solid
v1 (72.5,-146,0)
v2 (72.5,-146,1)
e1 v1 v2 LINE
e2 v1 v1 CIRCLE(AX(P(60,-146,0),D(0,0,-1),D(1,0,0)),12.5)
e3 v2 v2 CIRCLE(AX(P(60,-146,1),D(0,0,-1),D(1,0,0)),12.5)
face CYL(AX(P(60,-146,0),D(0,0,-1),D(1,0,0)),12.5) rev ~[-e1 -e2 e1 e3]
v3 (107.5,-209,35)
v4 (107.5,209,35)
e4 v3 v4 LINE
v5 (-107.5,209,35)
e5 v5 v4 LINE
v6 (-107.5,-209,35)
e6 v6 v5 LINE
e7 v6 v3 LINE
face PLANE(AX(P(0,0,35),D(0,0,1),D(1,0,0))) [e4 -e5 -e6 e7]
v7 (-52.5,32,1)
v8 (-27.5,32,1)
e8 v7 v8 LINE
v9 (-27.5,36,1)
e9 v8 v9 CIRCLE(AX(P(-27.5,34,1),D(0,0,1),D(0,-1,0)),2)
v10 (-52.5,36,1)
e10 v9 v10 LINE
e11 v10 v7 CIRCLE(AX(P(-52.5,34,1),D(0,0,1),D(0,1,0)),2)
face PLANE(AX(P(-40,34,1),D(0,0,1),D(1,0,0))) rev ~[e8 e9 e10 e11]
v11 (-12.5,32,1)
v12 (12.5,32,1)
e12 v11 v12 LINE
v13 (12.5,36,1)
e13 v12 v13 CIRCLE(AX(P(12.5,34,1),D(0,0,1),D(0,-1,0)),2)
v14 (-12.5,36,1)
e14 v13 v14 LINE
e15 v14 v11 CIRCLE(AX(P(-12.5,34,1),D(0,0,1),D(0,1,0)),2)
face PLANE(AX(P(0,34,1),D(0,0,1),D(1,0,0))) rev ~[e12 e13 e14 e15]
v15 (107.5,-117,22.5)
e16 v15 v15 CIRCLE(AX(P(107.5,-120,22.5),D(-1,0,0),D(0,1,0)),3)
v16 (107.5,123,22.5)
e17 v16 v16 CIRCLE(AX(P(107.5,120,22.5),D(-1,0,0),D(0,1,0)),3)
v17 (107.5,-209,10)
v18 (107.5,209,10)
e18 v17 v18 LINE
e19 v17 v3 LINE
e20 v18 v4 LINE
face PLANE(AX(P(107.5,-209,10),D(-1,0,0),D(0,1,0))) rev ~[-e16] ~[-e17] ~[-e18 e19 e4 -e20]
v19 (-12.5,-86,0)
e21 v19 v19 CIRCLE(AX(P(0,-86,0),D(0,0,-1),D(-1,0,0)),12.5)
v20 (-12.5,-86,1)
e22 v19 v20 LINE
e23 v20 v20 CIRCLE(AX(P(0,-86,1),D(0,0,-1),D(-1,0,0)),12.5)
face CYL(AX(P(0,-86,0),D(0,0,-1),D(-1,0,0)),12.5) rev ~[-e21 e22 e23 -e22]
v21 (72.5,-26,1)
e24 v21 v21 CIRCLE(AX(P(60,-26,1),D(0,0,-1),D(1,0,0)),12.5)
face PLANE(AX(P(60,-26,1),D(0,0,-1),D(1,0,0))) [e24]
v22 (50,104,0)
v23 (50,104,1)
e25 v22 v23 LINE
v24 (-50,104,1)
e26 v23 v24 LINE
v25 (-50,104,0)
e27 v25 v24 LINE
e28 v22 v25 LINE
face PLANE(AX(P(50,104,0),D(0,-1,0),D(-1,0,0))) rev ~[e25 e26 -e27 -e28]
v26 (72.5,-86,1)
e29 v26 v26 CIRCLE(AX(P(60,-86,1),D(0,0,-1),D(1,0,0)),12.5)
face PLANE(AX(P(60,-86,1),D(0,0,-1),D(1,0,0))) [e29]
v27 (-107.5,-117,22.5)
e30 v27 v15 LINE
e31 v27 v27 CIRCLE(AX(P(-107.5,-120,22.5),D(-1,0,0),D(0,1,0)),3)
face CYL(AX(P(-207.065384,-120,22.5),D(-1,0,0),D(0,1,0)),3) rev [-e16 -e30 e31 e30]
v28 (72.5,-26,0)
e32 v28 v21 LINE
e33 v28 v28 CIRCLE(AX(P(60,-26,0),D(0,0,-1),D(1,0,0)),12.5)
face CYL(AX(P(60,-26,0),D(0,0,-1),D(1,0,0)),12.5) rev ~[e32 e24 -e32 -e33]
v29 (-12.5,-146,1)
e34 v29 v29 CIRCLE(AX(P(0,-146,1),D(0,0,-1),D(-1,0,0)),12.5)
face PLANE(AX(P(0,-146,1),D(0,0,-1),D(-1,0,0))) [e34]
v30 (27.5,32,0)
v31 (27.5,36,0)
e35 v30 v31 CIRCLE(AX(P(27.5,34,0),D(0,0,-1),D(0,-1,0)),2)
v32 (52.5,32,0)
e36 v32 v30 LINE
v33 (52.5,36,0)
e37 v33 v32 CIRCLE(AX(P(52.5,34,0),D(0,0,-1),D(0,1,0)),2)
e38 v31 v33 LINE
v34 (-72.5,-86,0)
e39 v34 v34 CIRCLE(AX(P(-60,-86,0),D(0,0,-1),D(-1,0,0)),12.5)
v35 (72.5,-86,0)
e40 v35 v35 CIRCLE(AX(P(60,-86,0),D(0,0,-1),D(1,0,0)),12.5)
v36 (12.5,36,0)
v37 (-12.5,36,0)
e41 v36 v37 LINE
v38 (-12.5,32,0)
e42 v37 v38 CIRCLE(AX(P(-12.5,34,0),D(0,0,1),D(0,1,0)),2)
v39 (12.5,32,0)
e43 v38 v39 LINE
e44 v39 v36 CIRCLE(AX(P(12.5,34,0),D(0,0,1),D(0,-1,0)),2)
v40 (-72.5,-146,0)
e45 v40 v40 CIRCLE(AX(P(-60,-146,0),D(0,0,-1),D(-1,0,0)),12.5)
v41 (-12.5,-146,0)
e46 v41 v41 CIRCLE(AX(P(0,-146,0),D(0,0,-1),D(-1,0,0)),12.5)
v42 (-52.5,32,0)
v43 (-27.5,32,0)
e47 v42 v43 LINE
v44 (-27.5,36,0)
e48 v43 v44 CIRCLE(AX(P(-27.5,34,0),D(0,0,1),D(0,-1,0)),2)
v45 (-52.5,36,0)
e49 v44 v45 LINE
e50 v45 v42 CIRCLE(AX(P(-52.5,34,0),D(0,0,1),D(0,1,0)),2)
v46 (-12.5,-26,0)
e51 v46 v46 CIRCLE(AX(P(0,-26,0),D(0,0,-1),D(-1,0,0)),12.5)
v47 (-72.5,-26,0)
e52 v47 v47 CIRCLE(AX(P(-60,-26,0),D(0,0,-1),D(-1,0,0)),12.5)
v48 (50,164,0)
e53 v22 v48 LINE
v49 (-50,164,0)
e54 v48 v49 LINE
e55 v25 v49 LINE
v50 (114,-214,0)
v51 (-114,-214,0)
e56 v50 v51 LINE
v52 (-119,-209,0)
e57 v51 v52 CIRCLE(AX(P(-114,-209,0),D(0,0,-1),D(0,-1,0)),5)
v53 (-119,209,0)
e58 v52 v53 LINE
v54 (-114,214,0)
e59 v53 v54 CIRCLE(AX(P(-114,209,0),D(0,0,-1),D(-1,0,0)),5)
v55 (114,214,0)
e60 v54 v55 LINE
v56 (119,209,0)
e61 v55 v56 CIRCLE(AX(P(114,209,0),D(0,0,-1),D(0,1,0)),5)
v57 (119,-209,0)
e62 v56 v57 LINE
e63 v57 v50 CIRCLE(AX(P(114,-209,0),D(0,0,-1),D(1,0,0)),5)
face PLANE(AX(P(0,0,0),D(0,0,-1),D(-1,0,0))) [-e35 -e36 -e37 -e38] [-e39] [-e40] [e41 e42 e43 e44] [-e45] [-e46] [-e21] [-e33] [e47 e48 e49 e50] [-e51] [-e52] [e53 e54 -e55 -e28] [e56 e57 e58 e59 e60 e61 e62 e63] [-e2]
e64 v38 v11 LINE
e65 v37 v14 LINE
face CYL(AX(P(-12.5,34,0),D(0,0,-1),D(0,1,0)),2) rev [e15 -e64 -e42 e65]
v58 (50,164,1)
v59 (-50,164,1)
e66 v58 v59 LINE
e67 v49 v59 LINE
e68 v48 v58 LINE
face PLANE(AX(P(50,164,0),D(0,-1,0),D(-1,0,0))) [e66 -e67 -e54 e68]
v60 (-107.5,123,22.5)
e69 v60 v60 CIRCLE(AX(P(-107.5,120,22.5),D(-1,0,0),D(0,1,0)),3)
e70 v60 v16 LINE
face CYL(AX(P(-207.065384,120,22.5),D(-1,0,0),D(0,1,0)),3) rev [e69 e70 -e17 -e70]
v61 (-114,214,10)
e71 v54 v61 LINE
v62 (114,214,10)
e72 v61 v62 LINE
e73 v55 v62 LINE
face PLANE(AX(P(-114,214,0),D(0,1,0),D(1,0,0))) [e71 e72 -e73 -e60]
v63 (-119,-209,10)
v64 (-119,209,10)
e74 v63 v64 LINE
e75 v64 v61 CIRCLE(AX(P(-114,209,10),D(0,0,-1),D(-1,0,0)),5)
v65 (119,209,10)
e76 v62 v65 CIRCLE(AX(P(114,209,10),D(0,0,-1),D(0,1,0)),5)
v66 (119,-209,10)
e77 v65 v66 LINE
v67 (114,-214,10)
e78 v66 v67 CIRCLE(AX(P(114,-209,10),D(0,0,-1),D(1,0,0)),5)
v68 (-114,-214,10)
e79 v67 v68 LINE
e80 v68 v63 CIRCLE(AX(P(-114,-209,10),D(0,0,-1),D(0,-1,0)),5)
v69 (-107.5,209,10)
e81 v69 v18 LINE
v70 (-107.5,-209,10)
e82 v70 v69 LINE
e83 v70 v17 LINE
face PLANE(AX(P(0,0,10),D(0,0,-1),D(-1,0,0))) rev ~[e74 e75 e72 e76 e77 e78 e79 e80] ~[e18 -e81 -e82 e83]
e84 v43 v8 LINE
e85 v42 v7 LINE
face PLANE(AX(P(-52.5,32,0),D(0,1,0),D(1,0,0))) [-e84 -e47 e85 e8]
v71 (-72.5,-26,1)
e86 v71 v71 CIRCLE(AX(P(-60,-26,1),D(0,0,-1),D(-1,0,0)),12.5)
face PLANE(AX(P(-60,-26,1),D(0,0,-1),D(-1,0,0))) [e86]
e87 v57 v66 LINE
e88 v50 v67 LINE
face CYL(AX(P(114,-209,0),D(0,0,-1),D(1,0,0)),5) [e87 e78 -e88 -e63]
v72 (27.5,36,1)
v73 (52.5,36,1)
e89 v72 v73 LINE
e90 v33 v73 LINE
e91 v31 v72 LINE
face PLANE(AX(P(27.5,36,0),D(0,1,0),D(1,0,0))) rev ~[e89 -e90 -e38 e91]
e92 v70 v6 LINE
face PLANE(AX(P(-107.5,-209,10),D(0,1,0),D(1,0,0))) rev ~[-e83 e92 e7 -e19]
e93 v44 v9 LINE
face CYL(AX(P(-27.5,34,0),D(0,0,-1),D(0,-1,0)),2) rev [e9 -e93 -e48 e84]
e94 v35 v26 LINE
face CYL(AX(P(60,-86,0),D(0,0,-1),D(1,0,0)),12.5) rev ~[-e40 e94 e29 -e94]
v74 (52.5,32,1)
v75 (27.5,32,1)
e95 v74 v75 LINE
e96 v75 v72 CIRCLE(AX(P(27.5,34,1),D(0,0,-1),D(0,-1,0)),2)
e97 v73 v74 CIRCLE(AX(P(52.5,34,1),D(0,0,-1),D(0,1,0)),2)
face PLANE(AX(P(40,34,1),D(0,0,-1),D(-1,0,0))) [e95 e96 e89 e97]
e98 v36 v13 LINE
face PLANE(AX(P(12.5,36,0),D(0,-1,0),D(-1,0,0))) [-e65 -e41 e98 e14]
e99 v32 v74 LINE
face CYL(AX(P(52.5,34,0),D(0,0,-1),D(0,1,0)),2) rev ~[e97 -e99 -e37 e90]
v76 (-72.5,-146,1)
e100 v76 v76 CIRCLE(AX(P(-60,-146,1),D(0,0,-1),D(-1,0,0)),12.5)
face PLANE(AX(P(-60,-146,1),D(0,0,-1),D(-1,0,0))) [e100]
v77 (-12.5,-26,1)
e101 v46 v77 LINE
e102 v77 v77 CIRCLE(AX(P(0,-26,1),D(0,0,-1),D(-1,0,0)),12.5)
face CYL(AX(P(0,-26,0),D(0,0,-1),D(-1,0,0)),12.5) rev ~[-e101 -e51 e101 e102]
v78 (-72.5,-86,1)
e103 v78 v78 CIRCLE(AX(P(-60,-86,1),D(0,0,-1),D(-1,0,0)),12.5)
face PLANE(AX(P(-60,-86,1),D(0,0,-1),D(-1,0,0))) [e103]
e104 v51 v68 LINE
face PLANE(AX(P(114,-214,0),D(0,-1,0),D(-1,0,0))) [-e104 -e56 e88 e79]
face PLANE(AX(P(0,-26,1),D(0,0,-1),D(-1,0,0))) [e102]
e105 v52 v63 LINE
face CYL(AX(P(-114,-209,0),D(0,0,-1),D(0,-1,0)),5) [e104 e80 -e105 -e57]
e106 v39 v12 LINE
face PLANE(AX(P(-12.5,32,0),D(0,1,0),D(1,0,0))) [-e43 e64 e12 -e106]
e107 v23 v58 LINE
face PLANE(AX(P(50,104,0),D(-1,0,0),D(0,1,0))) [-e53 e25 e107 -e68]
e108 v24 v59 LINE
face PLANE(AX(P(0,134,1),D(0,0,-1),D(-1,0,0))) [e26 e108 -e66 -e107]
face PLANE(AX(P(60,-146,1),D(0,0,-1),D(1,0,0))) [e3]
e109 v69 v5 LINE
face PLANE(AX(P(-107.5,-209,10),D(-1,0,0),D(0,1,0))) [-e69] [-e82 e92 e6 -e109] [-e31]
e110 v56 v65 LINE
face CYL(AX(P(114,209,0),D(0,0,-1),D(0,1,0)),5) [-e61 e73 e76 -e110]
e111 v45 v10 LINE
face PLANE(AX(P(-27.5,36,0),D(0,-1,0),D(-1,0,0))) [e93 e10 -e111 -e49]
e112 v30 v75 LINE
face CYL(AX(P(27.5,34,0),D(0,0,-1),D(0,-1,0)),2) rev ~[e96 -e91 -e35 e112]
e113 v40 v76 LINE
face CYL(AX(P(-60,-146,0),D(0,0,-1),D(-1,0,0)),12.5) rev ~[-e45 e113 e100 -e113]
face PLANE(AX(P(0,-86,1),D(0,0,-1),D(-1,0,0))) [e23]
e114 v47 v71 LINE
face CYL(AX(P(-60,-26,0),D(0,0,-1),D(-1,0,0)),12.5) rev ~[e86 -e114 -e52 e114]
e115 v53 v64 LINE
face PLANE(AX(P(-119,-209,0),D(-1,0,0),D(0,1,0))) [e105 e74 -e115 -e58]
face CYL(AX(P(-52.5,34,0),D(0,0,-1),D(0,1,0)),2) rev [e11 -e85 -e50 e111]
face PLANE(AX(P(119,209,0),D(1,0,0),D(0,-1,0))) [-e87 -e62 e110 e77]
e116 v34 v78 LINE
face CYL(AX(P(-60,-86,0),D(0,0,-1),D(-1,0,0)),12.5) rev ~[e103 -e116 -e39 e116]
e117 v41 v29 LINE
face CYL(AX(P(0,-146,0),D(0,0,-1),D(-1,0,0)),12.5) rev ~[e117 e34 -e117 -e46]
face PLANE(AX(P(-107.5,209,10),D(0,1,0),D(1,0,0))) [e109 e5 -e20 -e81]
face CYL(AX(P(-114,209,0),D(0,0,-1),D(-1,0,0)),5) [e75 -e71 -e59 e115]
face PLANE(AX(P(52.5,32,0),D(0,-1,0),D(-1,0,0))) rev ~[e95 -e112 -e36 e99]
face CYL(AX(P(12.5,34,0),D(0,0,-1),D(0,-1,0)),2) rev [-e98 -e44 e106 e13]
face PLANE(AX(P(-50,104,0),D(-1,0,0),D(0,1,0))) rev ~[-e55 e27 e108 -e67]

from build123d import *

# Parameters (mm, degrees)
EXTRUDE_1_DEPTH          = 10
SKETCH_2_W               = 215
SKETCH_2_H               = 418
EXTRUDE_2_DEPTH          = 25
CUT_EXTRUDE_1_DEPTH      = 314.565383931
CUT_EXTRUDE_1_DEPTH_BACK = 314.565383931
SKETCH_3_R               = 3
SKETCH_4_R               = 12.5
SKETCH_4_W               = 100
SKETCH_4_H               = 60
CUT_EXTRUDE_2_DEPTH      = 1


with BuildPart() as part:
    # 草图1 → 凸台-拉伸1 (new body)
    with BuildSketch(Plane.XY):
        with BuildLine():
            Line((-114, 214), (114, 214))
            ThreePointArc((114, 214), (117.535533906, 212.535533906), (119, 209))
            Line((119, 209), (119, -209))
            ThreePointArc((119, -209), (117.535533906, -212.535533906), (114, -214))
            Line((114, -214), (-114, -214))
            ThreePointArc((-114, -214), (-117.535533906, -212.535533906), (-119, -209))
            Line((-119, -209), (-119, 209))
            ThreePointArc((-119, 209), (-117.535533906, 212.535533906), (-114, 214))
        make_face()
    extrude(amount=EXTRUDE_1_DEPTH)

    # 草图2 → 凸台-拉伸2 (add)
    with BuildSketch(Plane.XY.offset(10)):
        Rectangle(SKETCH_2_W, SKETCH_2_H)
    extrude(amount=EXTRUDE_2_DEPTH)

    # 草图3 → 切除-拉伸1 (cut, two sides: drawn at the far end of the back side and taken through both)
    with BuildSketch(Plane(origin=(107.5, 0, 0), x_dir=(0, 0, -1), z_dir=(1, 0, 0)).offset(-CUT_EXTRUDE_1_DEPTH_BACK)):
        with Locations(Location((-22.5, 120, 0), (0, 0, 90))):
            Circle(SKETCH_3_R)
        with Locations(Location((-22.5, -120, 0), (0, 0, 90))):
            Circle(SKETCH_3_R)
    extrude(amount=CUT_EXTRUDE_1_DEPTH + CUT_EXTRUDE_1_DEPTH_BACK, mode=Mode.SUBTRACT)

    # 草图4 → 切除-拉伸2 (cut)
    with BuildSketch(Plane(origin=(0, 0, 0), x_dir=(-1, 0, 0), z_dir=(0, 0, -1))):
        with Locations((0, -26)):
            Circle(SKETCH_4_R)
        with Locations((60, -26)):
            Circle(SKETCH_4_R)
        with Locations((60, -86)):
            Circle(SKETCH_4_R)
        with Locations((60, -146)):
            Circle(SKETCH_4_R)
        with Locations((0, -86)):
            Circle(SKETCH_4_R)
        with Locations((0, -146)):
            Circle(SKETCH_4_R)
        with Locations(Location((-60, -146, 0), (0, 0, 180))):
            Circle(SKETCH_4_R)
        with Locations(Location((-60, -86, 0), (0, 0, 180))):
            Circle(SKETCH_4_R)
        with Locations(Location((-60, -26, 0), (0, 0, 180))):
            Circle(SKETCH_4_R)
        with Locations((0, 134)):
            Rectangle(SKETCH_4_W, SKETCH_4_H)
        with BuildLine():
            Line((-12.5, 36), (12.5, 36))
            ThreePointArc((12.5, 36), (14.5, 34), (12.5, 32))
            Line((12.5, 32), (-12.5, 32))
            ThreePointArc((-12.5, 32), (-14.5, 34), (-12.5, 36))
        make_face()
        with BuildLine():
            Line((27.5, 36), (52.5, 36))
            ThreePointArc((52.5, 36), (54.5, 34), (52.5, 32))
            Line((52.5, 32), (27.5, 32))
            ThreePointArc((27.5, 32), (25.5, 34), (27.5, 36))
        make_face()
        with BuildLine():
            Line((-27.5, 36), (-52.5, 36))
            ThreePointArc((-52.5, 36), (-54.5, 34), (-52.5, 32))
            Line((-52.5, 32), (-27.5, 32))
            ThreePointArc((-27.5, 32), (-25.5, 34), (-27.5, 36))
        make_face()
    extrude(amount=-CUT_EXTRUDE_2_DEPTH, mode=Mode.SUBTRACT)


solid = part.part
